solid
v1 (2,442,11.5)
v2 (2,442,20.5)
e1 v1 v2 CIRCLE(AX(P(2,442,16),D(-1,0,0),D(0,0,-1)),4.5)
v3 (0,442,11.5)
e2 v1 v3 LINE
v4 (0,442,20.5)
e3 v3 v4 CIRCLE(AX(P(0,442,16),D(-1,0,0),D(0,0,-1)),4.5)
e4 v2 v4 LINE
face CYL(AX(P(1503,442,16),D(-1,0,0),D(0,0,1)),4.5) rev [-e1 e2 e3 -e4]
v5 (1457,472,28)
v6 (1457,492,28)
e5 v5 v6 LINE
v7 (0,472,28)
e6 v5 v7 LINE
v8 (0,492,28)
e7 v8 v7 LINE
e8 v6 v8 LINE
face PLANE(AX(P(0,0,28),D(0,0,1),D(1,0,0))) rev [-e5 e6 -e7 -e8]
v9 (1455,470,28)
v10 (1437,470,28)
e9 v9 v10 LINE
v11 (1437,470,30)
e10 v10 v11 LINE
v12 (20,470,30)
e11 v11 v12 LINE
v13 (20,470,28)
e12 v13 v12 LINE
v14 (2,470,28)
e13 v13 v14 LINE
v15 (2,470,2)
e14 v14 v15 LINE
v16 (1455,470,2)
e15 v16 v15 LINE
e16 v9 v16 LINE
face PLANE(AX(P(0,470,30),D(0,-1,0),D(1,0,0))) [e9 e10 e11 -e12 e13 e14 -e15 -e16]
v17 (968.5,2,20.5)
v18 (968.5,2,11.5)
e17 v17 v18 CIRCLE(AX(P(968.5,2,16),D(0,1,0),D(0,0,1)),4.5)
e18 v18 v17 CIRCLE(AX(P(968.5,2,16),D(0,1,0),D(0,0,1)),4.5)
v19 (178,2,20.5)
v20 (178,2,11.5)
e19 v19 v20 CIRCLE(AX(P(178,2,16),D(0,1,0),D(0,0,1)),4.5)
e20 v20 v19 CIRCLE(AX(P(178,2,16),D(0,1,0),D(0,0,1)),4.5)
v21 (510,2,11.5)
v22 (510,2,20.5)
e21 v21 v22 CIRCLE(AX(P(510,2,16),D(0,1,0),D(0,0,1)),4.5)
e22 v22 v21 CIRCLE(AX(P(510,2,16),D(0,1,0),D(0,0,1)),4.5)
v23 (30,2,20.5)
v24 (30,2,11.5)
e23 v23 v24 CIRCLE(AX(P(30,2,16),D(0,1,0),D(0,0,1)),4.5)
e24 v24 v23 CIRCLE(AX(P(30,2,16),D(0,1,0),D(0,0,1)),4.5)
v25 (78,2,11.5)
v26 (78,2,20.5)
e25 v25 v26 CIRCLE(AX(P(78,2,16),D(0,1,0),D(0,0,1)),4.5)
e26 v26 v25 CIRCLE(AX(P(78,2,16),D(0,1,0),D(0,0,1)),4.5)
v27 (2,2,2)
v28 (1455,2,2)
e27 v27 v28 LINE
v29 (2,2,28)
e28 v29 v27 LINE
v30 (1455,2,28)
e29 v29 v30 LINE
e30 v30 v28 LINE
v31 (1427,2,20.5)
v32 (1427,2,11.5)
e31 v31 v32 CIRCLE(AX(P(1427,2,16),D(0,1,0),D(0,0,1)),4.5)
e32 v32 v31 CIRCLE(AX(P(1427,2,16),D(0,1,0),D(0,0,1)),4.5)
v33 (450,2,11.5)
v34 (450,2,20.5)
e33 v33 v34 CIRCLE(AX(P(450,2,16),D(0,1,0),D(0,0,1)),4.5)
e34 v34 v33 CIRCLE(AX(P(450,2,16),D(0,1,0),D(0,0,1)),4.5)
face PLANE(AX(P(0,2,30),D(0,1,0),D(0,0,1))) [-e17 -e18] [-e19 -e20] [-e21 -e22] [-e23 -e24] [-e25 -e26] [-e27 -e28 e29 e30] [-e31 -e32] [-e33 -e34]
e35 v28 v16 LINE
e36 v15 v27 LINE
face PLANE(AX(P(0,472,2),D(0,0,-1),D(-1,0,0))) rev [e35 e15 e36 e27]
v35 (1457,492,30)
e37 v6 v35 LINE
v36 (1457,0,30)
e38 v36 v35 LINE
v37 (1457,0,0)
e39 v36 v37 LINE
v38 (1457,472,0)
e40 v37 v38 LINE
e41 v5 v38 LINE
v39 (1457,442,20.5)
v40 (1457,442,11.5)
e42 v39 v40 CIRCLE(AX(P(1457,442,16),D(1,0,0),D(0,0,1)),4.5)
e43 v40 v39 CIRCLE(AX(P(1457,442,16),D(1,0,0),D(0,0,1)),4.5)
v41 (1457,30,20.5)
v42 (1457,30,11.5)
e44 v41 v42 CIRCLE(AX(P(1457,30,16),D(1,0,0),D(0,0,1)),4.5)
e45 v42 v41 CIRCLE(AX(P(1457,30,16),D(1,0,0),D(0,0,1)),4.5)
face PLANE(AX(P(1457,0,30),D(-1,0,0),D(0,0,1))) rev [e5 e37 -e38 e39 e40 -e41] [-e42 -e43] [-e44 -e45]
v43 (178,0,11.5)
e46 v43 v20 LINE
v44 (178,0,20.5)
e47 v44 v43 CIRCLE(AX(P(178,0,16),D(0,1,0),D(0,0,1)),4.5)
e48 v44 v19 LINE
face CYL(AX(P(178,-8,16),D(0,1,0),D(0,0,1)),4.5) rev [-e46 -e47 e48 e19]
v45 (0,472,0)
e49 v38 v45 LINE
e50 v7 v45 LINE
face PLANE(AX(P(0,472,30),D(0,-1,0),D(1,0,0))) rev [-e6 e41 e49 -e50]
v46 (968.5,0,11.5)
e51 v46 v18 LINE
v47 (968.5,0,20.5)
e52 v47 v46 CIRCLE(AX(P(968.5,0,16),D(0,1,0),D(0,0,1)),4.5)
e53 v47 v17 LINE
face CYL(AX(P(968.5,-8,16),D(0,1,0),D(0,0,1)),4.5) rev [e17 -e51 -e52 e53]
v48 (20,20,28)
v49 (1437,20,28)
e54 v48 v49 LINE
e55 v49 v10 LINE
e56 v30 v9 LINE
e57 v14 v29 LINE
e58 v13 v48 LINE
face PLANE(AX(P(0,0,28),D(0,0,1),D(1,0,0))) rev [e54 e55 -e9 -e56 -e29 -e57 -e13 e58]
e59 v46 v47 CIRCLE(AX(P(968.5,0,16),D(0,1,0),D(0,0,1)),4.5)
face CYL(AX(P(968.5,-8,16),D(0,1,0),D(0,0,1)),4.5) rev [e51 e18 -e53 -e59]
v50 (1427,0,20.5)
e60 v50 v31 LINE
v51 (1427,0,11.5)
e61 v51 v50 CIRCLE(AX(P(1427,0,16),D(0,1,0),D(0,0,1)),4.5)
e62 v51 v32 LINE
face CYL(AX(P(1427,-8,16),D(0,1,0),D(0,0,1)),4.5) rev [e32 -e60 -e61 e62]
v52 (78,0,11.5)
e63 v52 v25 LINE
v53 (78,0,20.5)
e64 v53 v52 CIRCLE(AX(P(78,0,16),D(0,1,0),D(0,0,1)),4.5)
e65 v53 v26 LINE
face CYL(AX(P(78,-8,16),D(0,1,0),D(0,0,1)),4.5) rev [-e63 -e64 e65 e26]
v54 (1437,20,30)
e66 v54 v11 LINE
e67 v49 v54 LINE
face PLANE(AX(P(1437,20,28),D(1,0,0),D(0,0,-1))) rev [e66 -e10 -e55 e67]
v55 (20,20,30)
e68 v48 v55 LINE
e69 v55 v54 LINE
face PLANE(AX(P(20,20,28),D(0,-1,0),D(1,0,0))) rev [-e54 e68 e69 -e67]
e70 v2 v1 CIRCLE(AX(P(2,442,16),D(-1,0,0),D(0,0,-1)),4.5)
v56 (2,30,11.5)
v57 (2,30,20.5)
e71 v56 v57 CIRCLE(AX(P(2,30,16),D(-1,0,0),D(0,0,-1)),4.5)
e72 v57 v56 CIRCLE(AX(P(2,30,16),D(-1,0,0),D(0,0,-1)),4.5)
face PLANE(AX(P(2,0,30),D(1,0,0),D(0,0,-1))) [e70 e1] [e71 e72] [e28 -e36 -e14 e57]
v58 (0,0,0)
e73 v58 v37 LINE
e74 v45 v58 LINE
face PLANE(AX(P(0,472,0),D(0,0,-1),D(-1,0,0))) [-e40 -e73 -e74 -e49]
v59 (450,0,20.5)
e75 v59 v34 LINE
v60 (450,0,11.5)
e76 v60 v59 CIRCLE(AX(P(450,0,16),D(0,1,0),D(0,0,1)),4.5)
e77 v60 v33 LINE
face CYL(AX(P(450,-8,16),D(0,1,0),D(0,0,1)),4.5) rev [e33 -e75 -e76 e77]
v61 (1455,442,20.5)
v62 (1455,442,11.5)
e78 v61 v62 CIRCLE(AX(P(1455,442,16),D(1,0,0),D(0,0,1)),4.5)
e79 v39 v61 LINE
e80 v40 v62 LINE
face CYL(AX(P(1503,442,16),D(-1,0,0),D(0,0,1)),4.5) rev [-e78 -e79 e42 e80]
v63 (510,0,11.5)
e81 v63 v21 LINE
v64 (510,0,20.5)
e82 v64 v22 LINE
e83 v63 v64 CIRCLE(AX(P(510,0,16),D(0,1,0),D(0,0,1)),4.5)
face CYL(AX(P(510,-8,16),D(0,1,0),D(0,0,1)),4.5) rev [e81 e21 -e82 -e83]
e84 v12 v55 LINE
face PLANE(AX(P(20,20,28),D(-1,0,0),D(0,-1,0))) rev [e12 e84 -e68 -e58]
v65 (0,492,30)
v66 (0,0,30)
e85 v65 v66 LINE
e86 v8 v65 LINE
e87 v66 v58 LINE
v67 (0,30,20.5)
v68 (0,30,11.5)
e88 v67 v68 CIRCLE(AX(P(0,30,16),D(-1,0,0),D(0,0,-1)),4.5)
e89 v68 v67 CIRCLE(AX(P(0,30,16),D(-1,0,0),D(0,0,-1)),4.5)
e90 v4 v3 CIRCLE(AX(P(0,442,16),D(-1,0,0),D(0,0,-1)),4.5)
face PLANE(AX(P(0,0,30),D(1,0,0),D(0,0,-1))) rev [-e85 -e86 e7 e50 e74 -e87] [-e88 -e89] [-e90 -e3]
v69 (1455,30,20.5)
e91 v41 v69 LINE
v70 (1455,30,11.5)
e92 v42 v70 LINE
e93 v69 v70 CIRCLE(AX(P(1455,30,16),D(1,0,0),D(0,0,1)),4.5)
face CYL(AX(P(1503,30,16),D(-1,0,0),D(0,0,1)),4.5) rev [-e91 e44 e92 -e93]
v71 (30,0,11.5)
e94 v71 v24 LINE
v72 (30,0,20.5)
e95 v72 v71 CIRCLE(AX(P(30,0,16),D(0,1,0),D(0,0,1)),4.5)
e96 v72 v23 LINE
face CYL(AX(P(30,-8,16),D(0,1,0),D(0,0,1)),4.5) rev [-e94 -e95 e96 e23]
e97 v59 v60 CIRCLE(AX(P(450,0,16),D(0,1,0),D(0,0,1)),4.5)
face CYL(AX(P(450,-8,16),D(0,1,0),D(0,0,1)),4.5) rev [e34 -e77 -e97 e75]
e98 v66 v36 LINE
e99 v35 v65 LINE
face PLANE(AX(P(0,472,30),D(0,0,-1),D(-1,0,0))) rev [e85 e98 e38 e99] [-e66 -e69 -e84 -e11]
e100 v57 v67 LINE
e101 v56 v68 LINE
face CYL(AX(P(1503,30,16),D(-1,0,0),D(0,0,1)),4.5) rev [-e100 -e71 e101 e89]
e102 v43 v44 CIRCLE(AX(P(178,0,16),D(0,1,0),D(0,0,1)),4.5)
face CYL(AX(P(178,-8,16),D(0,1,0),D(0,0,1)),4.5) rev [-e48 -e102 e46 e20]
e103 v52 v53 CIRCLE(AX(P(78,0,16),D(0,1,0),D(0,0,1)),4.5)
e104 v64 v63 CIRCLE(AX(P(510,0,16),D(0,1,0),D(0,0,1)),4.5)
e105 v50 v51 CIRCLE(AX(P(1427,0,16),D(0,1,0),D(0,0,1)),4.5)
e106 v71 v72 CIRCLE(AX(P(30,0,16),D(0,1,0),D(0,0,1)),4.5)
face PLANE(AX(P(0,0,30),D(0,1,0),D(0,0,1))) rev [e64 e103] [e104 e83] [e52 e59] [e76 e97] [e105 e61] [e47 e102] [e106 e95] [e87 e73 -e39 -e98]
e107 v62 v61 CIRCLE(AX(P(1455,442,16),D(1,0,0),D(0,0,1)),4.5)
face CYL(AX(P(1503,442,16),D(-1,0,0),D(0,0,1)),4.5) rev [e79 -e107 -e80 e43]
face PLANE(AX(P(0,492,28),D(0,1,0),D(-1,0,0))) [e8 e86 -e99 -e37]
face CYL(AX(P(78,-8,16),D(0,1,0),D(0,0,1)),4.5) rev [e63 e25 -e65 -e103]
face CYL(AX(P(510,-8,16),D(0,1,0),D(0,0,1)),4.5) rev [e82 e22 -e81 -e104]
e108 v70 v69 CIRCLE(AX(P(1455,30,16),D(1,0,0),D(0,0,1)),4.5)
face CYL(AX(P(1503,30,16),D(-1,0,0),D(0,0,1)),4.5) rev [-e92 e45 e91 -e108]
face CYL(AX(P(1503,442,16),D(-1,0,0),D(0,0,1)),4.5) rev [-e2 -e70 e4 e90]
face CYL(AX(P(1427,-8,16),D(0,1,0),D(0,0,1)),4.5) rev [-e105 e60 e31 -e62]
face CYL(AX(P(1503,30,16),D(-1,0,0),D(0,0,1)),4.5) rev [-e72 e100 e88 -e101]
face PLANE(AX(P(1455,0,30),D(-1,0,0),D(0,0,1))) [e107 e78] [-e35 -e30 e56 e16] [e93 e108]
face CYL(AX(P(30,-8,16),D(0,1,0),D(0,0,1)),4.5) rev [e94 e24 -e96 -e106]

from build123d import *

# Parameters (mm, degrees)
SKETCH_1_W               = 1457
SKETCH_1_H               = 472
EXTRUDE_1_DEPTH          = 30
SHELL_1_T                = -2
SKETCH_2_W               = 1457
SKETCH_2_H               = 492
SKETCH_2_W_2             = 1417
SKETCH_2_H_2             = 450
EXTRUDE_2_DEPTH          = 2
CUT_EXTRUDE_1_DEPTH      = 1501
CUT_EXTRUDE_1_DEPTH_BACK = 10
SKETCH_3_R               = 4.5
SKETCH_6_R               = 4.5
CUT_EXTRUDE_2_DEPTH      = 10


with BuildPart() as part:
    # 草图1 → 凸台-拉伸1 (new body)
    with BuildSketch(Plane.XY):
        with Locations((728.5, 236)):
            Rectangle(SKETCH_1_W, SKETCH_1_H)
    extrude(amount=EXTRUDE_1_DEPTH)

    # 抽壳1
    shell_1_openings = [part.faces().sort_by_distance(p)[0] for p in [
        (728.5, 236, 30),
    ]]
    offset(amount=SHELL_1_T, openings=shell_1_openings, kind=Kind.INTERSECTION)

    # 草图2 → 凸台-拉伸2 (add)
    with BuildSketch(Plane.XY.offset(30)):
        with Locations((728.5, 246)):
            Rectangle(SKETCH_2_W, SKETCH_2_H)
        with Locations((728.5, 245)):
            Rectangle(SKETCH_2_W_2, SKETCH_2_H_2, mode=Mode.SUBTRACT)
    extrude(amount=-EXTRUDE_2_DEPTH)

    # 草图3 → 切除-拉伸1 (cut, two sides: drawn at the far end of the back side and taken through both)
    with BuildSketch(Plane(origin=(2, 0, 0), x_dir=(0, 0, -1), z_dir=(1, 0, 0)).offset(-CUT_EXTRUDE_1_DEPTH_BACK)):
        with Locations(Location((-16, 442, 0), (0, 0, 180))):
            Circle(SKETCH_3_R)
        with Locations(Location((-16, 30, 0), (0, 0, 180))):
            Circle(SKETCH_3_R)
    extrude(amount=CUT_EXTRUDE_1_DEPTH + CUT_EXTRUDE_1_DEPTH_BACK, mode=Mode.SUBTRACT)

    # 草图6 → 切除-拉伸2 (cut)
    with BuildSketch(Plane(origin=(0, 2, 0), x_dir=(1, 0, 0), z_dir=(0, 1, 0))):
        with Locations(Location((30, -16, 0), (0, 0, 270))):
            Circle(SKETCH_6_R)
        with Locations(Location((450, -16, 0), (0, 0, 270))):
            Circle(SKETCH_6_R)
        with Locations(Location((1427, -16, 0), (0, 0, 270))):
            Circle(SKETCH_6_R)
        with Locations(Location((968.5, -16, 0), (0, 0, 270))):
            Circle(SKETCH_6_R)
        with Locations(Location((510, -16, 0), (0, 0, 270))):
            Circle(SKETCH_6_R)
        with Locations(Location((78, -16, 0), (0, 0, 270))):
            Circle(SKETCH_6_R)
        with Locations(Location((178, -16, 0), (0, 0, 270))):
            Circle(SKETCH_6_R)
    extrude(amount=-CUT_EXTRUDE_2_DEPTH, mode=Mode.SUBTRACT)


solid = part.part
